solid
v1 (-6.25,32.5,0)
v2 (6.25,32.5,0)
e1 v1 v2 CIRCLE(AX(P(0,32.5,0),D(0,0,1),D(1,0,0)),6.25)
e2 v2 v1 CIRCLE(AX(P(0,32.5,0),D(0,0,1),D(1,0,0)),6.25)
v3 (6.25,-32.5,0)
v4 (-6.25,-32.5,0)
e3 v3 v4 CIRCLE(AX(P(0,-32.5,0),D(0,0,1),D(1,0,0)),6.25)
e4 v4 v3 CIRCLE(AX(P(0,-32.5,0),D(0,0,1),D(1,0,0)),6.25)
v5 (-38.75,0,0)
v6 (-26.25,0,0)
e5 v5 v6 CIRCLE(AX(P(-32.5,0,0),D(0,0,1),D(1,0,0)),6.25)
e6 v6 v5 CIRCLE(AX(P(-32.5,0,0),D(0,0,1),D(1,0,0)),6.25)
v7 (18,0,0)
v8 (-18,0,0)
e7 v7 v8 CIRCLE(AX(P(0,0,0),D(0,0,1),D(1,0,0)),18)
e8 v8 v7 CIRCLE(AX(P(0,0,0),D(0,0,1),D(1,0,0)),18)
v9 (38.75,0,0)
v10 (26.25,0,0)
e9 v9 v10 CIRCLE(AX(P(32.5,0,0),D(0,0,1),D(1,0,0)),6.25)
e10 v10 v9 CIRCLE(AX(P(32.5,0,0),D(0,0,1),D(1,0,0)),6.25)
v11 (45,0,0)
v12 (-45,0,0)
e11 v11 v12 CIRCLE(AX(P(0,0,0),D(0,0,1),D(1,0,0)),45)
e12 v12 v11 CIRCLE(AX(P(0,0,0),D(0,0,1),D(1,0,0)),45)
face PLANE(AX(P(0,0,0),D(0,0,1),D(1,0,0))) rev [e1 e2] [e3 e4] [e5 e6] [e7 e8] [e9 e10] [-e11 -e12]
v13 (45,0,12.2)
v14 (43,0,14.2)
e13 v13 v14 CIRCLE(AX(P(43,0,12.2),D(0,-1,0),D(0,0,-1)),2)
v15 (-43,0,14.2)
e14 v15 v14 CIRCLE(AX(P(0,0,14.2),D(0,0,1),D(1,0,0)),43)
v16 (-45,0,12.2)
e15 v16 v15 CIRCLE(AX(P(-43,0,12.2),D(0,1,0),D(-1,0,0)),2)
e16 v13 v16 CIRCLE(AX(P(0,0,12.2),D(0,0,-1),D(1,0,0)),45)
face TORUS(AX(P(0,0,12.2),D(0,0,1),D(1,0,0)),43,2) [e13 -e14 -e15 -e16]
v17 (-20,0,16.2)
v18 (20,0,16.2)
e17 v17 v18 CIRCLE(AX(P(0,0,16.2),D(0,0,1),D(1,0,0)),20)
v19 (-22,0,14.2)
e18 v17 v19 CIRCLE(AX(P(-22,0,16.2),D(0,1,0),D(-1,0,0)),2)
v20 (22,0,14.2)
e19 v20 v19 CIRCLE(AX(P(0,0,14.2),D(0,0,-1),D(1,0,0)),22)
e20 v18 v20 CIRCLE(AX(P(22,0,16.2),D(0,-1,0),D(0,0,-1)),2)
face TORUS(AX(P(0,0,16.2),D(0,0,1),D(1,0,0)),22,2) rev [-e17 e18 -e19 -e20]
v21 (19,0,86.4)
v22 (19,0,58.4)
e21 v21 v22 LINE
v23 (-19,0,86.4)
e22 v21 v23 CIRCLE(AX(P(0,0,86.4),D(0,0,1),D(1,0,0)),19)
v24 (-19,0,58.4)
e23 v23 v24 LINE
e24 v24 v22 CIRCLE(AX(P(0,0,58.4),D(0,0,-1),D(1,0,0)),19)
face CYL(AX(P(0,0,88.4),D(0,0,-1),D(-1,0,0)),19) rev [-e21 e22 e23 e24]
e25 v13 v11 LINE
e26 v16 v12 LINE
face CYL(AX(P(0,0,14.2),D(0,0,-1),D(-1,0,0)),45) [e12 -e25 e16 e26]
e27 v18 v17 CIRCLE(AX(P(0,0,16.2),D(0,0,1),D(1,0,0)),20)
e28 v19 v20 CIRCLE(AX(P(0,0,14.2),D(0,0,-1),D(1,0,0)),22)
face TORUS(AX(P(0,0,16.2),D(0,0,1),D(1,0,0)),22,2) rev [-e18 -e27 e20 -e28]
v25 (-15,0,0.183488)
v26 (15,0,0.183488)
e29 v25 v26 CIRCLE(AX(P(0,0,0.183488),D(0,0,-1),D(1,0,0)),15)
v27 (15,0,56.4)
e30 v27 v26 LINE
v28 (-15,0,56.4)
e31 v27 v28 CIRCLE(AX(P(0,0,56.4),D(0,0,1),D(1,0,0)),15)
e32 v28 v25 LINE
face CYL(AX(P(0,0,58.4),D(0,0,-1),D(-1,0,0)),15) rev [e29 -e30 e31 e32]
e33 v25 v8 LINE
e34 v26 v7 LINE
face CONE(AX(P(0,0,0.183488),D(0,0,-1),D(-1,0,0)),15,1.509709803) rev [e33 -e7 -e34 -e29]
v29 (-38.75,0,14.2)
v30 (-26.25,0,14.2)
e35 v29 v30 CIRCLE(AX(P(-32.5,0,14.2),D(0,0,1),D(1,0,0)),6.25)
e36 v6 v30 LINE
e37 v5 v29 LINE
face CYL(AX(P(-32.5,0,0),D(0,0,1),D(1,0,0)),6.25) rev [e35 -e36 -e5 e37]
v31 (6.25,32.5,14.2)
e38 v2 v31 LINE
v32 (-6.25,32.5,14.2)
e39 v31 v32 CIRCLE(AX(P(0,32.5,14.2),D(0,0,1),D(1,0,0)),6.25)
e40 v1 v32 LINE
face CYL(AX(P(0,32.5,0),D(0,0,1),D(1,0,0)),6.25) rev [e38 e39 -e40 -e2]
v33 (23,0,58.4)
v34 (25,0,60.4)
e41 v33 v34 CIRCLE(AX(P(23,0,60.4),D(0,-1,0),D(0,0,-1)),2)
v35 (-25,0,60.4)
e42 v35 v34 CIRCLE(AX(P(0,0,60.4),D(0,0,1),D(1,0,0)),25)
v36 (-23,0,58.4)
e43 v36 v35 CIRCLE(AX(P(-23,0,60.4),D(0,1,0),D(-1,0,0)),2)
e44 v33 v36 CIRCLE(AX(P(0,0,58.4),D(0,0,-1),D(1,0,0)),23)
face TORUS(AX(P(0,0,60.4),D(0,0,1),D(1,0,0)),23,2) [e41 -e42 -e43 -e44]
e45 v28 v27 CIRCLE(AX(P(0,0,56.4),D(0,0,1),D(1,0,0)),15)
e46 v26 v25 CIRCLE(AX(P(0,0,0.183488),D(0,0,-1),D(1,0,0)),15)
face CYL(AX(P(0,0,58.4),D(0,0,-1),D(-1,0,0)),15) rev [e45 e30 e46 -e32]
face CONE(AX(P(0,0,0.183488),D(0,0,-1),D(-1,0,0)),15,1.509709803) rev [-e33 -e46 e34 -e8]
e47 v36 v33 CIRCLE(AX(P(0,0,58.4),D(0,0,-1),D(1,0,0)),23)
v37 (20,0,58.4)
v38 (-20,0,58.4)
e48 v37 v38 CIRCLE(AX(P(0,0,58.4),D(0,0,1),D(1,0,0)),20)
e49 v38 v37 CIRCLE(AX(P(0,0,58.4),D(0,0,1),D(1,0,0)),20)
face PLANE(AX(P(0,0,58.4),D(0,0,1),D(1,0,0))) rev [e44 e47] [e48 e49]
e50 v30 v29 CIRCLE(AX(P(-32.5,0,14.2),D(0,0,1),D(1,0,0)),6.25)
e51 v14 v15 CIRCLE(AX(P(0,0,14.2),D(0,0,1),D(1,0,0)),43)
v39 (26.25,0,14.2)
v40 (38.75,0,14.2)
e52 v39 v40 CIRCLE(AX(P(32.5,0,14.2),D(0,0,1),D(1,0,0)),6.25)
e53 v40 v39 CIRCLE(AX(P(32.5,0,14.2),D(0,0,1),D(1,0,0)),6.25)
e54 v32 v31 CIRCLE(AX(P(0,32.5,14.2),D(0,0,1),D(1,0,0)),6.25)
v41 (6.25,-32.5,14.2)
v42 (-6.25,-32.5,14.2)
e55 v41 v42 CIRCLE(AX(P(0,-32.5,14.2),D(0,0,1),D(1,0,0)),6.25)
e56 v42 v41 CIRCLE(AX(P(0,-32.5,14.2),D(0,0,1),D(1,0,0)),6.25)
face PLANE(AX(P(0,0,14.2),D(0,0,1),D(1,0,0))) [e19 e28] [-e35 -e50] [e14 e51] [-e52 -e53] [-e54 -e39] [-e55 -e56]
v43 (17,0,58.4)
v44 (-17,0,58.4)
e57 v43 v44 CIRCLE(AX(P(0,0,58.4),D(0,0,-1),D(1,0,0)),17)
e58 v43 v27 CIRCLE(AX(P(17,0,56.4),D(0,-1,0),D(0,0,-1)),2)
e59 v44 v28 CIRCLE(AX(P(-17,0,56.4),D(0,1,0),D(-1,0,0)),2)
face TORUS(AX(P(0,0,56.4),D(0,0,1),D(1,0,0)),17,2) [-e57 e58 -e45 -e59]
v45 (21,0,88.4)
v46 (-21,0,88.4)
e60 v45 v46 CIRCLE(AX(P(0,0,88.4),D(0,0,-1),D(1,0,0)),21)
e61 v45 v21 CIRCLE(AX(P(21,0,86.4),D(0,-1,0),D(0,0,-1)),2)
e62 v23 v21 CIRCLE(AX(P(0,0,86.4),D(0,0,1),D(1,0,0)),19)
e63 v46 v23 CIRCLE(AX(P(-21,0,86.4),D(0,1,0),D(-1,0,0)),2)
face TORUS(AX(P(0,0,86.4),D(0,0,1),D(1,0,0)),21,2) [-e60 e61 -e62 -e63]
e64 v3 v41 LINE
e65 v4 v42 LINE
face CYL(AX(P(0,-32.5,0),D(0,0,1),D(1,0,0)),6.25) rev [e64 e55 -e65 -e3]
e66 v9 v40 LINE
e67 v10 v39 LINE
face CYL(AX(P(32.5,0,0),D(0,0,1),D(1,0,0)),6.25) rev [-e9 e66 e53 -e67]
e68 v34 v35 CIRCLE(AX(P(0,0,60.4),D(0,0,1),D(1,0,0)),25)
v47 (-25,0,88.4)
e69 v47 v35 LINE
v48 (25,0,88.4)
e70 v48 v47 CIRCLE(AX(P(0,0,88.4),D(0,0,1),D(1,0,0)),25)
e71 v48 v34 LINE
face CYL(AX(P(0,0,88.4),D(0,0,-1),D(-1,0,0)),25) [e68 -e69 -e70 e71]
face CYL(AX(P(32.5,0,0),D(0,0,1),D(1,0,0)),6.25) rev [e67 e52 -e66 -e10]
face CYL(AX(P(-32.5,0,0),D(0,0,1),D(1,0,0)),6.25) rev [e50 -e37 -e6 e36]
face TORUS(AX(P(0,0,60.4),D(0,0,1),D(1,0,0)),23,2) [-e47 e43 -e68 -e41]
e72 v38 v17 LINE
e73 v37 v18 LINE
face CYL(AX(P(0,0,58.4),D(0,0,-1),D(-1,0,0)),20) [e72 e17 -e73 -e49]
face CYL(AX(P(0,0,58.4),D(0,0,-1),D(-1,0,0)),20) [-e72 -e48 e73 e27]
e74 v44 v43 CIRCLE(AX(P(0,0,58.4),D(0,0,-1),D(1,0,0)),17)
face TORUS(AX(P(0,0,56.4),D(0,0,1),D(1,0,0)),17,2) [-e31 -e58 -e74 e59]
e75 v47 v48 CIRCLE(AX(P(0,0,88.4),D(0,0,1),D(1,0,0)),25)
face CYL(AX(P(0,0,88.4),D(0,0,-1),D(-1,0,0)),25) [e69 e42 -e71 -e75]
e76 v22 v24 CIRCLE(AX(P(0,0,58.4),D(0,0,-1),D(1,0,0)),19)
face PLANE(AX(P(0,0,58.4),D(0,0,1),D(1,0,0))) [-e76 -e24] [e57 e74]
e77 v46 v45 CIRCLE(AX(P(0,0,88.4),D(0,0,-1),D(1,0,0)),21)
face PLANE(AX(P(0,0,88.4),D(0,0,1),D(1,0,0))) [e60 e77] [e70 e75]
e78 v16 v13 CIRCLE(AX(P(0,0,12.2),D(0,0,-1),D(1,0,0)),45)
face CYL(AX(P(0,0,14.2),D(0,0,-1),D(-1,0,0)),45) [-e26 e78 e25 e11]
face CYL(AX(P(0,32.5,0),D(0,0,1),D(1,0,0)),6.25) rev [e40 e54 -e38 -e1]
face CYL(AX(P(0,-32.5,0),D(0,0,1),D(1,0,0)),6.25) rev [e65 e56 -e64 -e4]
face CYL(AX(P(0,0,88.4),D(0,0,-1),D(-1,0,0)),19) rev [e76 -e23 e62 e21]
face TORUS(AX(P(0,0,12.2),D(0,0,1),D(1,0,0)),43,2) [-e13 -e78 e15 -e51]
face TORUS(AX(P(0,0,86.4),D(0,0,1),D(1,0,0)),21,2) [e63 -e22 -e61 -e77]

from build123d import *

# Parameters (mm, degrees)
FLANGE_PROFILE_90_R        = 45
FLANGE_90_DEPTH            = 14.2
FLANGE_HOLES_SKETCH_R      = 6.25
FLANGE_HOLES_4X_12_5_DEPTH = 14.2
SHANK_PROFILE_40_R         = 20
SHANK_40_DEPTH             = 44.2
BORE_PROFILE_30_R          = 15
THROUGH_BORE_30_DEPTH      = 87.374533284
BORE_CHAMFER_3MM_SIZE      = 3
BORE_CHAMFER_3MM_SIZE2     = 0.18348786
COLLAR_PROFILE_50_38_R     = 25
COLLAR_PROFILE_50_38_R_2   = 19
END_COLLAR_50_DEPTH        = 30
FLANGE_EDGE_FILLET_R2_R    = 2
FLANGE_SHANK_FILLET_R2_R   = 2
COLLAR_FILLET_R2_A_R       = 2
SHANK_BORE_FILLET_R2_R     = 2
COLLAR_FILLET_R2_B_R       = 2


with BuildPart() as part:
    # Flange Profile Ø90 → Flange Ø90 (new body)
    with BuildSketch(Plane.XY):
        Circle(FLANGE_PROFILE_90_R)
    extrude(amount=FLANGE_90_DEPTH)

    # Flange Holes Sketch → Flange Holes 4xØ12.5 (cut)
    with BuildSketch(Plane.XY.offset(14.2)):
        with Locations((0, 32.5)):
            Circle(FLANGE_HOLES_SKETCH_R)
        with Locations((0, -32.5)):
            Circle(FLANGE_HOLES_SKETCH_R)
        with Locations((-32.5, 0)):
            Circle(FLANGE_HOLES_SKETCH_R)
        with Locations((32.5, 0)):
            Circle(FLANGE_HOLES_SKETCH_R)
    extrude(amount=-FLANGE_HOLES_4X_12_5_DEPTH, mode=Mode.SUBTRACT)

    # Shank Profile Ø40 → Shank Ø40 (add)
    with BuildSketch(Plane.XY.offset(14.2)):
        Circle(SHANK_PROFILE_40_R)
    extrude(amount=SHANK_40_DEPTH)

    # Bore Profile Ø30 → Through Bore Ø30 (cut, through all)
    with BuildSketch(Plane(origin=(0, 0, 0), x_dir=(-1, 0, 0), z_dir=(0, 0, -1))):
        Circle(BORE_PROFILE_30_R)
    extrude(amount=-THROUGH_BORE_30_DEPTH, mode=Mode.SUBTRACT)

    # Bore Chamfer 3mm
    bore_chamfer_3mm_edges = [part.edges().sort_by_distance(p)[0] for p in [
        (15, 0, 0),
    ]]
    bore_chamfer_3mm_side = [part.faces().sort_by_distance(p)[0] for p in [
        (-43.727207794, 0, 0),
    ]]
    chamfer(bore_chamfer_3mm_edges, length=BORE_CHAMFER_3MM_SIZE, length2=BORE_CHAMFER_3MM_SIZE2, reference=bore_chamfer_3mm_side[0])

    # Collar Profile Ø50-Ø38 → End Collar Ø50 (add)
    with BuildSketch(Plane.XY.offset(58.4)):
        Circle(COLLAR_PROFILE_50_38_R)
        Circle(COLLAR_PROFILE_50_38_R_2, mode=Mode.SUBTRACT)
    extrude(amount=END_COLLAR_50_DEPTH)

    # Flange Edge Fillet R2
    flange_edge_fillet_r2_edges = [part.edges().sort_by_distance(p)[0] for p in [
        (-45, 0, 14.2),
    ]]
    fillet(flange_edge_fillet_r2_edges, radius=FLANGE_EDGE_FILLET_R2_R)

    # Flange-Shank Fillet R2
    flange_shank_fillet_r2_edges = [part.edges().sort_by_distance(p)[0] for p in [
        (-20, 0, 14.2),
    ]]
    fillet(flange_shank_fillet_r2_edges, radius=FLANGE_SHANK_FILLET_R2_R)

    # Collar Fillet R2 A
    collar_fillet_r2_a_edges = [part.edges().sort_by_distance(p)[0] for p in [
        (-19, 0, 88.4),
    ]]
    fillet(collar_fillet_r2_a_edges, radius=COLLAR_FILLET_R2_A_R)

    # Shank Bore Fillet R2
    shank_bore_fillet_r2_edges = [part.edges().sort_by_distance(p)[0] for p in [
        (15, 0, 58.4),
    ]]
    fillet(shank_bore_fillet_r2_edges, radius=SHANK_BORE_FILLET_R2_R)

    # Collar Fillet R2 B
    collar_fillet_r2_b_edges = [part.edges().sort_by_distance(p)[0] for p in [
        (-25, 0, 58.4),
    ]]
    fillet(collar_fillet_r2_b_edges, radius=COLLAR_FILLET_R2_B_R)


solid = part.part
